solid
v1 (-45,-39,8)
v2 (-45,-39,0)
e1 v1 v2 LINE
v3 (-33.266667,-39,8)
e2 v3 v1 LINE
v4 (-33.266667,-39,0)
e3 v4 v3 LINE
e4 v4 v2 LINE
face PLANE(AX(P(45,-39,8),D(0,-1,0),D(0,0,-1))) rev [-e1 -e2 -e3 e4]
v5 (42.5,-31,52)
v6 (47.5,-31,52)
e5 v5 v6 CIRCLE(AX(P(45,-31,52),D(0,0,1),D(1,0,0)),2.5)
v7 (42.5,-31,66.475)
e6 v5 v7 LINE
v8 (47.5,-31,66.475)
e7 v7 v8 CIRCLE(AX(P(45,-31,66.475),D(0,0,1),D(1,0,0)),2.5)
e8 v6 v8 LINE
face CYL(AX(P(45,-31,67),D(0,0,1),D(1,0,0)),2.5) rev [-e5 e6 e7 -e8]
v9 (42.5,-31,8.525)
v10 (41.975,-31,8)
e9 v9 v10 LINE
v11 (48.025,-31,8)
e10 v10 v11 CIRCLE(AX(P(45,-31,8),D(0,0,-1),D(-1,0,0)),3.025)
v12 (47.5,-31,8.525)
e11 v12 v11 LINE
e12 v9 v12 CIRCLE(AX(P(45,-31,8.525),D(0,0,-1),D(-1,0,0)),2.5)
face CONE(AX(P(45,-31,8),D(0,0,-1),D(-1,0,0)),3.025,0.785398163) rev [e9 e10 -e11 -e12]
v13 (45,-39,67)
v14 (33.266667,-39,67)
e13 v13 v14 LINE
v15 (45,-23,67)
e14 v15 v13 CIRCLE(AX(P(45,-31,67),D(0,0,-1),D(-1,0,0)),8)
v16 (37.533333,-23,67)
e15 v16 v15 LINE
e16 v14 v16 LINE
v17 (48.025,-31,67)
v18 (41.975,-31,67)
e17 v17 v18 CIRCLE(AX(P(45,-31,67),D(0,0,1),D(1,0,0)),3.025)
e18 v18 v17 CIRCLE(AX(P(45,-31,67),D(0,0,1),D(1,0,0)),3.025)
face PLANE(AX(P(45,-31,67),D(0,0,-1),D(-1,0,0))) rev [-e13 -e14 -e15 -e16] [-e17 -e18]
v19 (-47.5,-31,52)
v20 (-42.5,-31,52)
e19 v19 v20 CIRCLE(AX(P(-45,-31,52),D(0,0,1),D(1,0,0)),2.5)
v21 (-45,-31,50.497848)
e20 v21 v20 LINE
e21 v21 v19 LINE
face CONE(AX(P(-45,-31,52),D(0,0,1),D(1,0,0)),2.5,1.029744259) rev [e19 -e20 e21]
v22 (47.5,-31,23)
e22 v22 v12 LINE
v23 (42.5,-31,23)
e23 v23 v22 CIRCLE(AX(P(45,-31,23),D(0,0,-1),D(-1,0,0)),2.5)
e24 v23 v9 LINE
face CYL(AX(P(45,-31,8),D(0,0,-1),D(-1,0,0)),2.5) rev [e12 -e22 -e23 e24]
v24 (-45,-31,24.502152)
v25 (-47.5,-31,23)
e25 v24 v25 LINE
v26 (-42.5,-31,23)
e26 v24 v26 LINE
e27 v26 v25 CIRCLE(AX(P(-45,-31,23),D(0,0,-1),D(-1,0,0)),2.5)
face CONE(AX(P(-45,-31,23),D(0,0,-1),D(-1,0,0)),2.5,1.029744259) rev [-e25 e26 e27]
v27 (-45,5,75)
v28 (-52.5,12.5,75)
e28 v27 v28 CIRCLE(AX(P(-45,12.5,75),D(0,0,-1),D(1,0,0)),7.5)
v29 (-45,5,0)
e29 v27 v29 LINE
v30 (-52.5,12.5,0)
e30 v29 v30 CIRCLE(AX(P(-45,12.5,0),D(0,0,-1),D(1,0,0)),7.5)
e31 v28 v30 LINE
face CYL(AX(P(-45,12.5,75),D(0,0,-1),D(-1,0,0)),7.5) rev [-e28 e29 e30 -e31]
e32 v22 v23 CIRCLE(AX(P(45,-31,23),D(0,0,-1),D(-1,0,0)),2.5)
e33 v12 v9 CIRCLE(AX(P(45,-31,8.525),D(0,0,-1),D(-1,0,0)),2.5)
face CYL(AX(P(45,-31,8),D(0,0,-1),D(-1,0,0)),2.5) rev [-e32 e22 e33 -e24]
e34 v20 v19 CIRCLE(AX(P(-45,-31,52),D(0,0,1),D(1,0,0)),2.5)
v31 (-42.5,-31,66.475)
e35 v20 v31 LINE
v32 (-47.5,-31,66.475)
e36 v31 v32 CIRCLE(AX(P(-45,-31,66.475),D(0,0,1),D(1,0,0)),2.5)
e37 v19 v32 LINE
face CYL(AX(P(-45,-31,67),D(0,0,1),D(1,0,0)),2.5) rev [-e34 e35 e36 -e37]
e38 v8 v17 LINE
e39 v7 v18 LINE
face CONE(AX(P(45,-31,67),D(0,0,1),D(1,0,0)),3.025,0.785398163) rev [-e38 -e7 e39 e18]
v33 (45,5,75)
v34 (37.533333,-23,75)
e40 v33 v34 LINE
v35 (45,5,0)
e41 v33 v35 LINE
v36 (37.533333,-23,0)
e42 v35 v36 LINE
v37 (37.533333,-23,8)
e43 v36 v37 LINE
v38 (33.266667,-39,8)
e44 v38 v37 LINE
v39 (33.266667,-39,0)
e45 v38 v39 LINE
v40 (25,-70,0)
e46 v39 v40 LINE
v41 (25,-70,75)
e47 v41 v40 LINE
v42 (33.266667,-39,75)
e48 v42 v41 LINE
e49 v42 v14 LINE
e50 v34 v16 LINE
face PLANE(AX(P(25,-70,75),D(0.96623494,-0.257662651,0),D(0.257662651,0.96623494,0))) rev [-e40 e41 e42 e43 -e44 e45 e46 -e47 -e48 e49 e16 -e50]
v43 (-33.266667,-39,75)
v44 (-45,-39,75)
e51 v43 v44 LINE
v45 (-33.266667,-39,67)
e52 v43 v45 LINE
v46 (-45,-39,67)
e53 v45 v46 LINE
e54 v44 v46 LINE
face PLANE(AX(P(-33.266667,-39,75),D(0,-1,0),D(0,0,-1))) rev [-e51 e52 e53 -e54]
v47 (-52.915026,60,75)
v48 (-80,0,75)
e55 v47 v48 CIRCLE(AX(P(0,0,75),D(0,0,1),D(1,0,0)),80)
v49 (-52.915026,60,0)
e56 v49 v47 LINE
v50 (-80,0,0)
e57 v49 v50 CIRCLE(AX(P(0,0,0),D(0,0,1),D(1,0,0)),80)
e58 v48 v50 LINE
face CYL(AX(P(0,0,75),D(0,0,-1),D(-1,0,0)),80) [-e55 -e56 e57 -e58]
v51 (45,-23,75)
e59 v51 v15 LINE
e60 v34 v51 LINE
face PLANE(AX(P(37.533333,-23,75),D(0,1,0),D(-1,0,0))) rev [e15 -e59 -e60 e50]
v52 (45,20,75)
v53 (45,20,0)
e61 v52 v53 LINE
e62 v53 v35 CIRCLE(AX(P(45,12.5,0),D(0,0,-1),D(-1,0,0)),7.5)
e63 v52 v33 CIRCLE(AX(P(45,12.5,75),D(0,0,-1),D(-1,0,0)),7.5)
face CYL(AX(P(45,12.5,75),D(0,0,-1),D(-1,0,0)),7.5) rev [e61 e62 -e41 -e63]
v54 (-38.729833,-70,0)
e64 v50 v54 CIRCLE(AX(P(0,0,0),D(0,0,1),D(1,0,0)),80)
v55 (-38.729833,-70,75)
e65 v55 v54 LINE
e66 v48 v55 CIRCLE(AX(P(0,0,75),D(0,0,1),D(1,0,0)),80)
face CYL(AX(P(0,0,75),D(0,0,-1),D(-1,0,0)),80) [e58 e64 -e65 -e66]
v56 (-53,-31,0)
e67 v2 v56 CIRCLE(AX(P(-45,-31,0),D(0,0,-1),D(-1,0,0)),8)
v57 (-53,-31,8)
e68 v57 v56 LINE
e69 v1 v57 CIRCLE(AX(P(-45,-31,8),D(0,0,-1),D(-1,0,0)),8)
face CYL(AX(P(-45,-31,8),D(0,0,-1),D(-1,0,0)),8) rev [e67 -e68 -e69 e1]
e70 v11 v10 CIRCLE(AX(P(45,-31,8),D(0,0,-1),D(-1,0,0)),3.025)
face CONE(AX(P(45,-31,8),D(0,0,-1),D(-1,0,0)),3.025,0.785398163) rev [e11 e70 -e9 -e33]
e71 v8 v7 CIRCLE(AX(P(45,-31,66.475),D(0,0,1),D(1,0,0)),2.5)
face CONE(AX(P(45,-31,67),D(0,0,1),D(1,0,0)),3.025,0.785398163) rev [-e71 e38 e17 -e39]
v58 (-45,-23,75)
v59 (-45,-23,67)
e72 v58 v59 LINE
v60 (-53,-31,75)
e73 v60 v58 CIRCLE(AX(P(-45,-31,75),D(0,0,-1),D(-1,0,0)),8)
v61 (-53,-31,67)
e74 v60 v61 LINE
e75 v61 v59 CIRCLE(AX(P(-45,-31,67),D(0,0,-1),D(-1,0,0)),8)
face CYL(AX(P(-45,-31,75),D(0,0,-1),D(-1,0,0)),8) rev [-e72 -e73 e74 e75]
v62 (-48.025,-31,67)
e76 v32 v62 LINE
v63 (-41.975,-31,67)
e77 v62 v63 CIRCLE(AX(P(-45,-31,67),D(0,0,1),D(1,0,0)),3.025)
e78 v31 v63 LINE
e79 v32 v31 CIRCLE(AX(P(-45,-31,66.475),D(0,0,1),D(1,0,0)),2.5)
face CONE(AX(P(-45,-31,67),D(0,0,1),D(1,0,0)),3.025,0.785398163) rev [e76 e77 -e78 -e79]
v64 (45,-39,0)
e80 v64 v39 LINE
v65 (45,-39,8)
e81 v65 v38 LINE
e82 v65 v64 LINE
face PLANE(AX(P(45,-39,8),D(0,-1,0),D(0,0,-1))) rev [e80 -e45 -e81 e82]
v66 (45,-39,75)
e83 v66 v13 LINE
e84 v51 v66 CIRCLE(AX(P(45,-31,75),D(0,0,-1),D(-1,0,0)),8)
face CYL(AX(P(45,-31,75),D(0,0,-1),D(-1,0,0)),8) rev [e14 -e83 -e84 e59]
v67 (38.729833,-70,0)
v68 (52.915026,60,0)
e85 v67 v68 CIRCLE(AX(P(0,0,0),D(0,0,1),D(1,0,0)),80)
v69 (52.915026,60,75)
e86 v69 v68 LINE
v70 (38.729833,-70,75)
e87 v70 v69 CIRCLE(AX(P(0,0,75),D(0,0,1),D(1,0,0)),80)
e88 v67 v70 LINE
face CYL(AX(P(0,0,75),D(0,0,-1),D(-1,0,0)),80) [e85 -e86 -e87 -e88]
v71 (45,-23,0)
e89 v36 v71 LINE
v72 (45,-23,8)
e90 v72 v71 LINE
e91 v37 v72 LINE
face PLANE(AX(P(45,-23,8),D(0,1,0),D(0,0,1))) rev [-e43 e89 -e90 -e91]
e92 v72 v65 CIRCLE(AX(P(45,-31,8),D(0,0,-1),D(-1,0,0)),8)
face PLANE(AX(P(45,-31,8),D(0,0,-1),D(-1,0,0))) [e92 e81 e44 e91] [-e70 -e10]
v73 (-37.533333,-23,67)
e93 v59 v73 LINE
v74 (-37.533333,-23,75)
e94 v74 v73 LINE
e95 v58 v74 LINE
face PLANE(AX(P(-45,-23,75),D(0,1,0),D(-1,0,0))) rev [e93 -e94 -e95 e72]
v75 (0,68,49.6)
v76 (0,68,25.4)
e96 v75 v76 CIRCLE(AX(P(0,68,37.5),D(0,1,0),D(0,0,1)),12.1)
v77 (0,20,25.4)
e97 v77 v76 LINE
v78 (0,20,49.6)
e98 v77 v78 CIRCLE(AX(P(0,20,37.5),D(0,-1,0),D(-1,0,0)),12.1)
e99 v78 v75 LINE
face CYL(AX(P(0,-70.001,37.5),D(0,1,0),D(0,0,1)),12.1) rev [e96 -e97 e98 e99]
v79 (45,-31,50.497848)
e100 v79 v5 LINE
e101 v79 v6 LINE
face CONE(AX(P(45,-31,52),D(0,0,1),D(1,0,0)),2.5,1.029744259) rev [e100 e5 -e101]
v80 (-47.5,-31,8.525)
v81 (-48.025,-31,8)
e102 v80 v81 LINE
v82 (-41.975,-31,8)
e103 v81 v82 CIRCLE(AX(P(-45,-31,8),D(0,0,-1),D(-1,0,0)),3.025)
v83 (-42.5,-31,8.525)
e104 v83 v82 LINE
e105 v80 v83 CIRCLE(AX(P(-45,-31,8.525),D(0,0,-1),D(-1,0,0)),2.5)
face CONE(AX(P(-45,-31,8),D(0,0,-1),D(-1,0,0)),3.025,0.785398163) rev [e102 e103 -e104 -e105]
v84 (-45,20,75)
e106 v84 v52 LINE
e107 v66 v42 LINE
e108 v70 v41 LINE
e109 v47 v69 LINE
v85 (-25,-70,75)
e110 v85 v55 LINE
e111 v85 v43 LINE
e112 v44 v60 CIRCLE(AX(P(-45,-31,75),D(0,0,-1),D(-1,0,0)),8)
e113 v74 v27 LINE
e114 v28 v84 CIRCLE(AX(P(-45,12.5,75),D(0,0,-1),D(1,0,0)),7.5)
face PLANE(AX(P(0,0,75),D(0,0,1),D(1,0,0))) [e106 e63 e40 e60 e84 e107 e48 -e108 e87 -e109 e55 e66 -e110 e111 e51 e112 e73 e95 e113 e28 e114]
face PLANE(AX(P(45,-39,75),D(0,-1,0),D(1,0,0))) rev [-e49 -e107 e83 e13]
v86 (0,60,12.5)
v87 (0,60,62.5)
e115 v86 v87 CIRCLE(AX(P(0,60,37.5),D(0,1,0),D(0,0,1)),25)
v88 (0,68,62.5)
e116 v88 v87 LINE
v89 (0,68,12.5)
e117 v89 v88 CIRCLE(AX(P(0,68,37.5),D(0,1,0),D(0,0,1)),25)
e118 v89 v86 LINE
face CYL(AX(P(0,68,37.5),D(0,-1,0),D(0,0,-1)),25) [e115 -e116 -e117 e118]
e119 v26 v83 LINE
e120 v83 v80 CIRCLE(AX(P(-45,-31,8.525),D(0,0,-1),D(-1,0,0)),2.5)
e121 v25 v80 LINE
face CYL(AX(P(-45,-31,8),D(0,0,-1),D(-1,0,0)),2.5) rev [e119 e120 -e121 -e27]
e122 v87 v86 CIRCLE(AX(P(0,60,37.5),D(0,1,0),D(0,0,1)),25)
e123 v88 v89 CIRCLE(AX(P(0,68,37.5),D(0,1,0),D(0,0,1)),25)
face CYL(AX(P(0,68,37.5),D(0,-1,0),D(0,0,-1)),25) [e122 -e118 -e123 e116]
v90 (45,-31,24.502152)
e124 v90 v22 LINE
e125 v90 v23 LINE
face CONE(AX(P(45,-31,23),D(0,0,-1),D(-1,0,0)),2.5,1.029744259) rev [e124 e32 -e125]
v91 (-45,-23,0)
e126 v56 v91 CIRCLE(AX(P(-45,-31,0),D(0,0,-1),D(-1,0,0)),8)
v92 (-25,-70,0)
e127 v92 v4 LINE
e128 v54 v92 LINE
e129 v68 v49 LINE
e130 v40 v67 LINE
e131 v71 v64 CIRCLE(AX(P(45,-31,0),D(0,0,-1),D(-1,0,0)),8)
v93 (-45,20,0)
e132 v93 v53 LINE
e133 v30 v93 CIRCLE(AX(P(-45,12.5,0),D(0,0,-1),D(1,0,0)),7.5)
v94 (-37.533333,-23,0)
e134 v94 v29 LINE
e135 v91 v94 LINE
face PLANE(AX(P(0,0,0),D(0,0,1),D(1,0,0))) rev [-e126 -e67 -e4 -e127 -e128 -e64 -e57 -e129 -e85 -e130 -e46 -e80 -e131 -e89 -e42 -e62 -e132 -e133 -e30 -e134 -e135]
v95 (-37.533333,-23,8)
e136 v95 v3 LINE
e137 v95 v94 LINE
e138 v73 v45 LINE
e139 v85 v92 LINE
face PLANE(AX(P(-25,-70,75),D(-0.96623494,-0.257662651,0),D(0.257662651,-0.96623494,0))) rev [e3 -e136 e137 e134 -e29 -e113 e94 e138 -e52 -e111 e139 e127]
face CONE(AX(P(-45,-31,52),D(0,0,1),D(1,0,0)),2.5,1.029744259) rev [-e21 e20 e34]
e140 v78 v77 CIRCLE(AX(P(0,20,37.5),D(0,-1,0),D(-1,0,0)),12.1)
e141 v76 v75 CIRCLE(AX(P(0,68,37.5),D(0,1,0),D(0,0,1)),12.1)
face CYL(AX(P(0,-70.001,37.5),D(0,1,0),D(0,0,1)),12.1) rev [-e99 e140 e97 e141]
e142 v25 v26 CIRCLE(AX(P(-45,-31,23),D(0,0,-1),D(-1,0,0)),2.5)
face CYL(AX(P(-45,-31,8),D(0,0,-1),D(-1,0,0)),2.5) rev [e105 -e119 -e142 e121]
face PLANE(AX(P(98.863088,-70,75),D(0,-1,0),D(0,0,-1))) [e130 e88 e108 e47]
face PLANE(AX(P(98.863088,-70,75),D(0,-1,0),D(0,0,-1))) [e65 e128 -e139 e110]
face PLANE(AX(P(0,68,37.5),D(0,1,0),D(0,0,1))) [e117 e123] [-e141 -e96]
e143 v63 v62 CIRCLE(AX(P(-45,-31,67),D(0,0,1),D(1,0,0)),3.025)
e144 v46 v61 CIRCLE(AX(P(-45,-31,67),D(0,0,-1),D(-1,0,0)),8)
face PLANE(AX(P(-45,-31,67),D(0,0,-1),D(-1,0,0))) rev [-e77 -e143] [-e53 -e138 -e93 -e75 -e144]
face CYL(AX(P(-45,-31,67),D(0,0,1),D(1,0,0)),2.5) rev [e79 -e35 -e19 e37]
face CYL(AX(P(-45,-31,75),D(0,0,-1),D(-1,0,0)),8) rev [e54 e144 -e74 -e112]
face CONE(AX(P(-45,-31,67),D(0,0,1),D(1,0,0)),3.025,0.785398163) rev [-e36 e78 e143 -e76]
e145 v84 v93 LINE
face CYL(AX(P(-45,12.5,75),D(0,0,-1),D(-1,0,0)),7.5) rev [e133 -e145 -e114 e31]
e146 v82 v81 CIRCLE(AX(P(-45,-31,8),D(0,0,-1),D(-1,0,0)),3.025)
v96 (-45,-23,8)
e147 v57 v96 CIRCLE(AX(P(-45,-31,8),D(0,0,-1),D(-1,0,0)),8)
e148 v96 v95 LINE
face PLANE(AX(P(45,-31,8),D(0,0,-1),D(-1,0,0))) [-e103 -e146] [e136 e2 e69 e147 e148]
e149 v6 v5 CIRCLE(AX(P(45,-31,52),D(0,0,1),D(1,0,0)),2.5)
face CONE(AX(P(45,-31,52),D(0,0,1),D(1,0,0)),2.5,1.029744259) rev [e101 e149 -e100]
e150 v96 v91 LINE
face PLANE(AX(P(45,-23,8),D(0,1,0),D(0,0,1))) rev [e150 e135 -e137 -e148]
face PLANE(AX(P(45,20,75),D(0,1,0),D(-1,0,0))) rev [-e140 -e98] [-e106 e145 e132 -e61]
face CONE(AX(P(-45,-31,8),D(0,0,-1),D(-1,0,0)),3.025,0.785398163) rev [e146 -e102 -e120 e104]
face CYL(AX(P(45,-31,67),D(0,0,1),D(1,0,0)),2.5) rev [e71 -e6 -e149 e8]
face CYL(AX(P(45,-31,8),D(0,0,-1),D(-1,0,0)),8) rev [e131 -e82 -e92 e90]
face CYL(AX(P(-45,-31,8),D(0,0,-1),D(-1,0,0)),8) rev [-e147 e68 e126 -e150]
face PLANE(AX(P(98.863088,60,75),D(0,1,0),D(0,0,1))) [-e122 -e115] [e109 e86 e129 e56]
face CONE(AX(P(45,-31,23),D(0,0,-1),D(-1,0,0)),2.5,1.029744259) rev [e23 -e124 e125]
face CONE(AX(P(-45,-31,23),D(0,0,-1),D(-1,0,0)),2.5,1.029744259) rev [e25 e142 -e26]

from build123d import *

# Parameters (mm, degrees)
SKETCH1_R                             = 80
BOSS_EXTRUDE1_DEPTH                   = 75
SKETCH2_OUTSIDE_W                     = 209.676
SKETCH2_OUTSIDE_H                     = 209.676
SKETCH2_OUTSIDE_W_2                   = 199.64377861
SKETCH2_OUTSIDE_H_2                   = 130
CUT_EXTRUDE1_DEPTH                    = 136.738719605
CUT_EXTRUDE2_DEPTH                    = 131.096118313
CUT_EXTRUDE3_DEPTH                    = 8
CUT_EXTRUDE4_START                    = -59
CUT_EXTRUDE4_DEPTH                    = 8
M6_TAPPED_HOLE1_D                     = 5
M6_TAPPED_HOLE1_DEPTH                 = 15
M6_TAPPED_HOLE1_CSINK_D               = 6.05
M6_TAPPED_HOLE1_CSINK_ANGLE           = 90
M6_TAPPED_HOLE1_TIP                   = 1.502151548
M6_TAPPED_HOLE1_ON_FACE_2_D           = 5
M6_TAPPED_HOLE1_ON_FACE_2_DEPTH       = 15
M6_TAPPED_HOLE1_ON_FACE_2_CSINK_D     = 6.05
M6_TAPPED_HOLE1_ON_FACE_2_CSINK_ANGLE = 90
M6_TAPPED_HOLE1_ON_FACE_2_TIP         = 1.502151548
CUT_EXTRUDE5_REACH                    = 172.074
SKETCH7_R                             = 12.1
BOSS_EXTRUDE4_START                   = 8
SKETCH8_R                             = 25
SKETCH8_R_2                           = 12.1
BOSS_EXTRUDE4_DEPTH                   = 8


with BuildPart() as part:
    # Sketch1 → Boss-Extrude1 (new body)
    with BuildSketch(Plane.XY):
        Circle(SKETCH1_R)
    extrude(amount=BOSS_EXTRUDE1_DEPTH)

    # Sketch2 outside → Cut-Extrude1 (cut, through all)
    with BuildSketch(Plane(origin=(0, 0, 0), x_dir=(-1, 0, 0), z_dir=(0, 0, -1))):
        Rectangle(SKETCH2_OUTSIDE_W, SKETCH2_OUTSIDE_H)
        with Locations((0.958801498, -5)):
            Rectangle(SKETCH2_OUTSIDE_W_2, SKETCH2_OUTSIDE_H_2, mode=Mode.SUBTRACT)
    extrude(amount=-CUT_EXTRUDE1_DEPTH, mode=Mode.SUBTRACT)

    # Sketch3 → Cut-Extrude2 (cut, through all)
    with BuildSketch(Plane(origin=(0, 0, 0), x_dir=(-1, 0, 0), z_dir=(0, 0, -1))):
        with BuildLine():
            Line((-25, -70), (-45, 5))
            ThreePointArc((-45, 5), (-52.5, 12.5), (-45, 20))
            Line((-45, 20), (45, 20))
            ThreePointArc((45, 20), (52.5, 12.5), (45, 5))
            Line((45, 5), (25, -70))
            Line((25, -70), (-25, -70))
        make_face()
    extrude(amount=-CUT_EXTRUDE2_DEPTH, mode=Mode.SUBTRACT)

    # Sketch4 → Cut-Extrude3 (cut)
    with BuildSketch(Plane(origin=(0, 0, 0), x_dir=(-1, 0, 0), z_dir=(0, 0, -1))):
        with BuildLine():
            Line((-45, -23), (45, -23))
            ThreePointArc((45, -23), (53, -31), (45, -39))
            Line((45, -39), (-45, -39))
            ThreePointArc((-45, -39), (-53, -31), (-45, -23))
        make_face()
    extrude(amount=-CUT_EXTRUDE3_DEPTH, mode=Mode.SUBTRACT)

    # Sketch5 → Cut-Extrude4 (cut)
    with BuildSketch(Plane(origin=(0, 0, 8), x_dir=(-1, 0, 0), z_dir=(0, 0, -1)).offset(CUT_EXTRUDE4_START)):
        with BuildLine():
            Line((37.533333333, -23), (33.266666667, -39))
            Line((33.266666667, -39), (45, -39))
            ThreePointArc((45, -39), (53, -31), (45, -23))
            Line((45, -23), (37.533333333, -23))
        make_face()
        with BuildLine():
            Line((-33.266666667, -39), (-37.533333333, -23))
            Line((-37.533333333, -23), (-45, -23))
            ThreePointArc((-45, -23), (-53, -31), (-45, -39))
            Line((-45, -39), (-33.266666667, -39))
        make_face()
    extrude(amount=-CUT_EXTRUDE4_DEPTH, mode=Mode.SUBTRACT)

    # M6 Tapped Hole1
    with Locations(Plane(origin=(45, -31, 8), x_dir=(-1, 0, 0), z_dir=(0, 0, -1))):
        with Locations((0, 0), (90, 0)):
            CounterSinkHole(M6_TAPPED_HOLE1_D / 2, M6_TAPPED_HOLE1_CSINK_D / 2, depth=M6_TAPPED_HOLE1_DEPTH, counter_sink_angle=M6_TAPPED_HOLE1_CSINK_ANGLE)
            with Locations((0, 0, -(M6_TAPPED_HOLE1_DEPTH + M6_TAPPED_HOLE1_TIP / 2))):  # 118° drill point
                Cone(0, M6_TAPPED_HOLE1_D / 2, M6_TAPPED_HOLE1_TIP, mode=Mode.SUBTRACT)

    # M6 Tapped Hole1 on face 2
    with Locations(Plane(origin=(-45, -31, 67), x_dir=(1, 0, 0), z_dir=(0, 0, 1))):
        with Locations((0, 0), (90, 0)):
            CounterSinkHole(M6_TAPPED_HOLE1_ON_FACE_2_D / 2, M6_TAPPED_HOLE1_ON_FACE_2_CSINK_D / 2, depth=M6_TAPPED_HOLE1_ON_FACE_2_DEPTH, counter_sink_angle=M6_TAPPED_HOLE1_ON_FACE_2_CSINK_ANGLE)
            with Locations((0, 0, -(M6_TAPPED_HOLE1_ON_FACE_2_DEPTH + M6_TAPPED_HOLE1_ON_FACE_2_TIP / 2))):  # 118° drill point
                Cone(0, M6_TAPPED_HOLE1_ON_FACE_2_D / 2, M6_TAPPED_HOLE1_ON_FACE_2_TIP, mode=Mode.SUBTRACT)

    # Sketch7 → Cut-Extrude5 (cut, up to next)
    with BuildSketch(Plane(origin=(0, 60, 0), x_dir=(1, 0, 0), z_dir=(0, 1, 0)), mode=Mode.PRIVATE) as cut_extrude5_sk1:
        with Locations(Location((0, -37.5, 0), (0, 0, 270))):
            Circle(SKETCH7_R)
    cut_extrude5_tool1 = extrude(cut_extrude5_sk1.sketch, amount=-CUT_EXTRUDE5_REACH, mode=Mode.PRIVATE) & part.part
    add(cut_extrude5_tool1.solids().sort_by_distance((0, 60, 37.5))[0], mode=Mode.SUBTRACT)

    # Sketch8 → Boss-Extrude4 (add)
    with BuildSketch(Plane(origin=(0, 60, 0), x_dir=(1, 0, 0), z_dir=(0, 1, 0)).offset(BOSS_EXTRUDE4_START)):
        with Locations(Location((0, -37.5, 0), (0, 0, 270))):
            Circle(SKETCH8_R)
        with Locations(Location((0, -37.5, 0), (0, 0, 270))):
            Circle(SKETCH8_R_2, mode=Mode.SUBTRACT)
    extrude(amount=-BOSS_EXTRUDE4_DEPTH)


solid = part.part
